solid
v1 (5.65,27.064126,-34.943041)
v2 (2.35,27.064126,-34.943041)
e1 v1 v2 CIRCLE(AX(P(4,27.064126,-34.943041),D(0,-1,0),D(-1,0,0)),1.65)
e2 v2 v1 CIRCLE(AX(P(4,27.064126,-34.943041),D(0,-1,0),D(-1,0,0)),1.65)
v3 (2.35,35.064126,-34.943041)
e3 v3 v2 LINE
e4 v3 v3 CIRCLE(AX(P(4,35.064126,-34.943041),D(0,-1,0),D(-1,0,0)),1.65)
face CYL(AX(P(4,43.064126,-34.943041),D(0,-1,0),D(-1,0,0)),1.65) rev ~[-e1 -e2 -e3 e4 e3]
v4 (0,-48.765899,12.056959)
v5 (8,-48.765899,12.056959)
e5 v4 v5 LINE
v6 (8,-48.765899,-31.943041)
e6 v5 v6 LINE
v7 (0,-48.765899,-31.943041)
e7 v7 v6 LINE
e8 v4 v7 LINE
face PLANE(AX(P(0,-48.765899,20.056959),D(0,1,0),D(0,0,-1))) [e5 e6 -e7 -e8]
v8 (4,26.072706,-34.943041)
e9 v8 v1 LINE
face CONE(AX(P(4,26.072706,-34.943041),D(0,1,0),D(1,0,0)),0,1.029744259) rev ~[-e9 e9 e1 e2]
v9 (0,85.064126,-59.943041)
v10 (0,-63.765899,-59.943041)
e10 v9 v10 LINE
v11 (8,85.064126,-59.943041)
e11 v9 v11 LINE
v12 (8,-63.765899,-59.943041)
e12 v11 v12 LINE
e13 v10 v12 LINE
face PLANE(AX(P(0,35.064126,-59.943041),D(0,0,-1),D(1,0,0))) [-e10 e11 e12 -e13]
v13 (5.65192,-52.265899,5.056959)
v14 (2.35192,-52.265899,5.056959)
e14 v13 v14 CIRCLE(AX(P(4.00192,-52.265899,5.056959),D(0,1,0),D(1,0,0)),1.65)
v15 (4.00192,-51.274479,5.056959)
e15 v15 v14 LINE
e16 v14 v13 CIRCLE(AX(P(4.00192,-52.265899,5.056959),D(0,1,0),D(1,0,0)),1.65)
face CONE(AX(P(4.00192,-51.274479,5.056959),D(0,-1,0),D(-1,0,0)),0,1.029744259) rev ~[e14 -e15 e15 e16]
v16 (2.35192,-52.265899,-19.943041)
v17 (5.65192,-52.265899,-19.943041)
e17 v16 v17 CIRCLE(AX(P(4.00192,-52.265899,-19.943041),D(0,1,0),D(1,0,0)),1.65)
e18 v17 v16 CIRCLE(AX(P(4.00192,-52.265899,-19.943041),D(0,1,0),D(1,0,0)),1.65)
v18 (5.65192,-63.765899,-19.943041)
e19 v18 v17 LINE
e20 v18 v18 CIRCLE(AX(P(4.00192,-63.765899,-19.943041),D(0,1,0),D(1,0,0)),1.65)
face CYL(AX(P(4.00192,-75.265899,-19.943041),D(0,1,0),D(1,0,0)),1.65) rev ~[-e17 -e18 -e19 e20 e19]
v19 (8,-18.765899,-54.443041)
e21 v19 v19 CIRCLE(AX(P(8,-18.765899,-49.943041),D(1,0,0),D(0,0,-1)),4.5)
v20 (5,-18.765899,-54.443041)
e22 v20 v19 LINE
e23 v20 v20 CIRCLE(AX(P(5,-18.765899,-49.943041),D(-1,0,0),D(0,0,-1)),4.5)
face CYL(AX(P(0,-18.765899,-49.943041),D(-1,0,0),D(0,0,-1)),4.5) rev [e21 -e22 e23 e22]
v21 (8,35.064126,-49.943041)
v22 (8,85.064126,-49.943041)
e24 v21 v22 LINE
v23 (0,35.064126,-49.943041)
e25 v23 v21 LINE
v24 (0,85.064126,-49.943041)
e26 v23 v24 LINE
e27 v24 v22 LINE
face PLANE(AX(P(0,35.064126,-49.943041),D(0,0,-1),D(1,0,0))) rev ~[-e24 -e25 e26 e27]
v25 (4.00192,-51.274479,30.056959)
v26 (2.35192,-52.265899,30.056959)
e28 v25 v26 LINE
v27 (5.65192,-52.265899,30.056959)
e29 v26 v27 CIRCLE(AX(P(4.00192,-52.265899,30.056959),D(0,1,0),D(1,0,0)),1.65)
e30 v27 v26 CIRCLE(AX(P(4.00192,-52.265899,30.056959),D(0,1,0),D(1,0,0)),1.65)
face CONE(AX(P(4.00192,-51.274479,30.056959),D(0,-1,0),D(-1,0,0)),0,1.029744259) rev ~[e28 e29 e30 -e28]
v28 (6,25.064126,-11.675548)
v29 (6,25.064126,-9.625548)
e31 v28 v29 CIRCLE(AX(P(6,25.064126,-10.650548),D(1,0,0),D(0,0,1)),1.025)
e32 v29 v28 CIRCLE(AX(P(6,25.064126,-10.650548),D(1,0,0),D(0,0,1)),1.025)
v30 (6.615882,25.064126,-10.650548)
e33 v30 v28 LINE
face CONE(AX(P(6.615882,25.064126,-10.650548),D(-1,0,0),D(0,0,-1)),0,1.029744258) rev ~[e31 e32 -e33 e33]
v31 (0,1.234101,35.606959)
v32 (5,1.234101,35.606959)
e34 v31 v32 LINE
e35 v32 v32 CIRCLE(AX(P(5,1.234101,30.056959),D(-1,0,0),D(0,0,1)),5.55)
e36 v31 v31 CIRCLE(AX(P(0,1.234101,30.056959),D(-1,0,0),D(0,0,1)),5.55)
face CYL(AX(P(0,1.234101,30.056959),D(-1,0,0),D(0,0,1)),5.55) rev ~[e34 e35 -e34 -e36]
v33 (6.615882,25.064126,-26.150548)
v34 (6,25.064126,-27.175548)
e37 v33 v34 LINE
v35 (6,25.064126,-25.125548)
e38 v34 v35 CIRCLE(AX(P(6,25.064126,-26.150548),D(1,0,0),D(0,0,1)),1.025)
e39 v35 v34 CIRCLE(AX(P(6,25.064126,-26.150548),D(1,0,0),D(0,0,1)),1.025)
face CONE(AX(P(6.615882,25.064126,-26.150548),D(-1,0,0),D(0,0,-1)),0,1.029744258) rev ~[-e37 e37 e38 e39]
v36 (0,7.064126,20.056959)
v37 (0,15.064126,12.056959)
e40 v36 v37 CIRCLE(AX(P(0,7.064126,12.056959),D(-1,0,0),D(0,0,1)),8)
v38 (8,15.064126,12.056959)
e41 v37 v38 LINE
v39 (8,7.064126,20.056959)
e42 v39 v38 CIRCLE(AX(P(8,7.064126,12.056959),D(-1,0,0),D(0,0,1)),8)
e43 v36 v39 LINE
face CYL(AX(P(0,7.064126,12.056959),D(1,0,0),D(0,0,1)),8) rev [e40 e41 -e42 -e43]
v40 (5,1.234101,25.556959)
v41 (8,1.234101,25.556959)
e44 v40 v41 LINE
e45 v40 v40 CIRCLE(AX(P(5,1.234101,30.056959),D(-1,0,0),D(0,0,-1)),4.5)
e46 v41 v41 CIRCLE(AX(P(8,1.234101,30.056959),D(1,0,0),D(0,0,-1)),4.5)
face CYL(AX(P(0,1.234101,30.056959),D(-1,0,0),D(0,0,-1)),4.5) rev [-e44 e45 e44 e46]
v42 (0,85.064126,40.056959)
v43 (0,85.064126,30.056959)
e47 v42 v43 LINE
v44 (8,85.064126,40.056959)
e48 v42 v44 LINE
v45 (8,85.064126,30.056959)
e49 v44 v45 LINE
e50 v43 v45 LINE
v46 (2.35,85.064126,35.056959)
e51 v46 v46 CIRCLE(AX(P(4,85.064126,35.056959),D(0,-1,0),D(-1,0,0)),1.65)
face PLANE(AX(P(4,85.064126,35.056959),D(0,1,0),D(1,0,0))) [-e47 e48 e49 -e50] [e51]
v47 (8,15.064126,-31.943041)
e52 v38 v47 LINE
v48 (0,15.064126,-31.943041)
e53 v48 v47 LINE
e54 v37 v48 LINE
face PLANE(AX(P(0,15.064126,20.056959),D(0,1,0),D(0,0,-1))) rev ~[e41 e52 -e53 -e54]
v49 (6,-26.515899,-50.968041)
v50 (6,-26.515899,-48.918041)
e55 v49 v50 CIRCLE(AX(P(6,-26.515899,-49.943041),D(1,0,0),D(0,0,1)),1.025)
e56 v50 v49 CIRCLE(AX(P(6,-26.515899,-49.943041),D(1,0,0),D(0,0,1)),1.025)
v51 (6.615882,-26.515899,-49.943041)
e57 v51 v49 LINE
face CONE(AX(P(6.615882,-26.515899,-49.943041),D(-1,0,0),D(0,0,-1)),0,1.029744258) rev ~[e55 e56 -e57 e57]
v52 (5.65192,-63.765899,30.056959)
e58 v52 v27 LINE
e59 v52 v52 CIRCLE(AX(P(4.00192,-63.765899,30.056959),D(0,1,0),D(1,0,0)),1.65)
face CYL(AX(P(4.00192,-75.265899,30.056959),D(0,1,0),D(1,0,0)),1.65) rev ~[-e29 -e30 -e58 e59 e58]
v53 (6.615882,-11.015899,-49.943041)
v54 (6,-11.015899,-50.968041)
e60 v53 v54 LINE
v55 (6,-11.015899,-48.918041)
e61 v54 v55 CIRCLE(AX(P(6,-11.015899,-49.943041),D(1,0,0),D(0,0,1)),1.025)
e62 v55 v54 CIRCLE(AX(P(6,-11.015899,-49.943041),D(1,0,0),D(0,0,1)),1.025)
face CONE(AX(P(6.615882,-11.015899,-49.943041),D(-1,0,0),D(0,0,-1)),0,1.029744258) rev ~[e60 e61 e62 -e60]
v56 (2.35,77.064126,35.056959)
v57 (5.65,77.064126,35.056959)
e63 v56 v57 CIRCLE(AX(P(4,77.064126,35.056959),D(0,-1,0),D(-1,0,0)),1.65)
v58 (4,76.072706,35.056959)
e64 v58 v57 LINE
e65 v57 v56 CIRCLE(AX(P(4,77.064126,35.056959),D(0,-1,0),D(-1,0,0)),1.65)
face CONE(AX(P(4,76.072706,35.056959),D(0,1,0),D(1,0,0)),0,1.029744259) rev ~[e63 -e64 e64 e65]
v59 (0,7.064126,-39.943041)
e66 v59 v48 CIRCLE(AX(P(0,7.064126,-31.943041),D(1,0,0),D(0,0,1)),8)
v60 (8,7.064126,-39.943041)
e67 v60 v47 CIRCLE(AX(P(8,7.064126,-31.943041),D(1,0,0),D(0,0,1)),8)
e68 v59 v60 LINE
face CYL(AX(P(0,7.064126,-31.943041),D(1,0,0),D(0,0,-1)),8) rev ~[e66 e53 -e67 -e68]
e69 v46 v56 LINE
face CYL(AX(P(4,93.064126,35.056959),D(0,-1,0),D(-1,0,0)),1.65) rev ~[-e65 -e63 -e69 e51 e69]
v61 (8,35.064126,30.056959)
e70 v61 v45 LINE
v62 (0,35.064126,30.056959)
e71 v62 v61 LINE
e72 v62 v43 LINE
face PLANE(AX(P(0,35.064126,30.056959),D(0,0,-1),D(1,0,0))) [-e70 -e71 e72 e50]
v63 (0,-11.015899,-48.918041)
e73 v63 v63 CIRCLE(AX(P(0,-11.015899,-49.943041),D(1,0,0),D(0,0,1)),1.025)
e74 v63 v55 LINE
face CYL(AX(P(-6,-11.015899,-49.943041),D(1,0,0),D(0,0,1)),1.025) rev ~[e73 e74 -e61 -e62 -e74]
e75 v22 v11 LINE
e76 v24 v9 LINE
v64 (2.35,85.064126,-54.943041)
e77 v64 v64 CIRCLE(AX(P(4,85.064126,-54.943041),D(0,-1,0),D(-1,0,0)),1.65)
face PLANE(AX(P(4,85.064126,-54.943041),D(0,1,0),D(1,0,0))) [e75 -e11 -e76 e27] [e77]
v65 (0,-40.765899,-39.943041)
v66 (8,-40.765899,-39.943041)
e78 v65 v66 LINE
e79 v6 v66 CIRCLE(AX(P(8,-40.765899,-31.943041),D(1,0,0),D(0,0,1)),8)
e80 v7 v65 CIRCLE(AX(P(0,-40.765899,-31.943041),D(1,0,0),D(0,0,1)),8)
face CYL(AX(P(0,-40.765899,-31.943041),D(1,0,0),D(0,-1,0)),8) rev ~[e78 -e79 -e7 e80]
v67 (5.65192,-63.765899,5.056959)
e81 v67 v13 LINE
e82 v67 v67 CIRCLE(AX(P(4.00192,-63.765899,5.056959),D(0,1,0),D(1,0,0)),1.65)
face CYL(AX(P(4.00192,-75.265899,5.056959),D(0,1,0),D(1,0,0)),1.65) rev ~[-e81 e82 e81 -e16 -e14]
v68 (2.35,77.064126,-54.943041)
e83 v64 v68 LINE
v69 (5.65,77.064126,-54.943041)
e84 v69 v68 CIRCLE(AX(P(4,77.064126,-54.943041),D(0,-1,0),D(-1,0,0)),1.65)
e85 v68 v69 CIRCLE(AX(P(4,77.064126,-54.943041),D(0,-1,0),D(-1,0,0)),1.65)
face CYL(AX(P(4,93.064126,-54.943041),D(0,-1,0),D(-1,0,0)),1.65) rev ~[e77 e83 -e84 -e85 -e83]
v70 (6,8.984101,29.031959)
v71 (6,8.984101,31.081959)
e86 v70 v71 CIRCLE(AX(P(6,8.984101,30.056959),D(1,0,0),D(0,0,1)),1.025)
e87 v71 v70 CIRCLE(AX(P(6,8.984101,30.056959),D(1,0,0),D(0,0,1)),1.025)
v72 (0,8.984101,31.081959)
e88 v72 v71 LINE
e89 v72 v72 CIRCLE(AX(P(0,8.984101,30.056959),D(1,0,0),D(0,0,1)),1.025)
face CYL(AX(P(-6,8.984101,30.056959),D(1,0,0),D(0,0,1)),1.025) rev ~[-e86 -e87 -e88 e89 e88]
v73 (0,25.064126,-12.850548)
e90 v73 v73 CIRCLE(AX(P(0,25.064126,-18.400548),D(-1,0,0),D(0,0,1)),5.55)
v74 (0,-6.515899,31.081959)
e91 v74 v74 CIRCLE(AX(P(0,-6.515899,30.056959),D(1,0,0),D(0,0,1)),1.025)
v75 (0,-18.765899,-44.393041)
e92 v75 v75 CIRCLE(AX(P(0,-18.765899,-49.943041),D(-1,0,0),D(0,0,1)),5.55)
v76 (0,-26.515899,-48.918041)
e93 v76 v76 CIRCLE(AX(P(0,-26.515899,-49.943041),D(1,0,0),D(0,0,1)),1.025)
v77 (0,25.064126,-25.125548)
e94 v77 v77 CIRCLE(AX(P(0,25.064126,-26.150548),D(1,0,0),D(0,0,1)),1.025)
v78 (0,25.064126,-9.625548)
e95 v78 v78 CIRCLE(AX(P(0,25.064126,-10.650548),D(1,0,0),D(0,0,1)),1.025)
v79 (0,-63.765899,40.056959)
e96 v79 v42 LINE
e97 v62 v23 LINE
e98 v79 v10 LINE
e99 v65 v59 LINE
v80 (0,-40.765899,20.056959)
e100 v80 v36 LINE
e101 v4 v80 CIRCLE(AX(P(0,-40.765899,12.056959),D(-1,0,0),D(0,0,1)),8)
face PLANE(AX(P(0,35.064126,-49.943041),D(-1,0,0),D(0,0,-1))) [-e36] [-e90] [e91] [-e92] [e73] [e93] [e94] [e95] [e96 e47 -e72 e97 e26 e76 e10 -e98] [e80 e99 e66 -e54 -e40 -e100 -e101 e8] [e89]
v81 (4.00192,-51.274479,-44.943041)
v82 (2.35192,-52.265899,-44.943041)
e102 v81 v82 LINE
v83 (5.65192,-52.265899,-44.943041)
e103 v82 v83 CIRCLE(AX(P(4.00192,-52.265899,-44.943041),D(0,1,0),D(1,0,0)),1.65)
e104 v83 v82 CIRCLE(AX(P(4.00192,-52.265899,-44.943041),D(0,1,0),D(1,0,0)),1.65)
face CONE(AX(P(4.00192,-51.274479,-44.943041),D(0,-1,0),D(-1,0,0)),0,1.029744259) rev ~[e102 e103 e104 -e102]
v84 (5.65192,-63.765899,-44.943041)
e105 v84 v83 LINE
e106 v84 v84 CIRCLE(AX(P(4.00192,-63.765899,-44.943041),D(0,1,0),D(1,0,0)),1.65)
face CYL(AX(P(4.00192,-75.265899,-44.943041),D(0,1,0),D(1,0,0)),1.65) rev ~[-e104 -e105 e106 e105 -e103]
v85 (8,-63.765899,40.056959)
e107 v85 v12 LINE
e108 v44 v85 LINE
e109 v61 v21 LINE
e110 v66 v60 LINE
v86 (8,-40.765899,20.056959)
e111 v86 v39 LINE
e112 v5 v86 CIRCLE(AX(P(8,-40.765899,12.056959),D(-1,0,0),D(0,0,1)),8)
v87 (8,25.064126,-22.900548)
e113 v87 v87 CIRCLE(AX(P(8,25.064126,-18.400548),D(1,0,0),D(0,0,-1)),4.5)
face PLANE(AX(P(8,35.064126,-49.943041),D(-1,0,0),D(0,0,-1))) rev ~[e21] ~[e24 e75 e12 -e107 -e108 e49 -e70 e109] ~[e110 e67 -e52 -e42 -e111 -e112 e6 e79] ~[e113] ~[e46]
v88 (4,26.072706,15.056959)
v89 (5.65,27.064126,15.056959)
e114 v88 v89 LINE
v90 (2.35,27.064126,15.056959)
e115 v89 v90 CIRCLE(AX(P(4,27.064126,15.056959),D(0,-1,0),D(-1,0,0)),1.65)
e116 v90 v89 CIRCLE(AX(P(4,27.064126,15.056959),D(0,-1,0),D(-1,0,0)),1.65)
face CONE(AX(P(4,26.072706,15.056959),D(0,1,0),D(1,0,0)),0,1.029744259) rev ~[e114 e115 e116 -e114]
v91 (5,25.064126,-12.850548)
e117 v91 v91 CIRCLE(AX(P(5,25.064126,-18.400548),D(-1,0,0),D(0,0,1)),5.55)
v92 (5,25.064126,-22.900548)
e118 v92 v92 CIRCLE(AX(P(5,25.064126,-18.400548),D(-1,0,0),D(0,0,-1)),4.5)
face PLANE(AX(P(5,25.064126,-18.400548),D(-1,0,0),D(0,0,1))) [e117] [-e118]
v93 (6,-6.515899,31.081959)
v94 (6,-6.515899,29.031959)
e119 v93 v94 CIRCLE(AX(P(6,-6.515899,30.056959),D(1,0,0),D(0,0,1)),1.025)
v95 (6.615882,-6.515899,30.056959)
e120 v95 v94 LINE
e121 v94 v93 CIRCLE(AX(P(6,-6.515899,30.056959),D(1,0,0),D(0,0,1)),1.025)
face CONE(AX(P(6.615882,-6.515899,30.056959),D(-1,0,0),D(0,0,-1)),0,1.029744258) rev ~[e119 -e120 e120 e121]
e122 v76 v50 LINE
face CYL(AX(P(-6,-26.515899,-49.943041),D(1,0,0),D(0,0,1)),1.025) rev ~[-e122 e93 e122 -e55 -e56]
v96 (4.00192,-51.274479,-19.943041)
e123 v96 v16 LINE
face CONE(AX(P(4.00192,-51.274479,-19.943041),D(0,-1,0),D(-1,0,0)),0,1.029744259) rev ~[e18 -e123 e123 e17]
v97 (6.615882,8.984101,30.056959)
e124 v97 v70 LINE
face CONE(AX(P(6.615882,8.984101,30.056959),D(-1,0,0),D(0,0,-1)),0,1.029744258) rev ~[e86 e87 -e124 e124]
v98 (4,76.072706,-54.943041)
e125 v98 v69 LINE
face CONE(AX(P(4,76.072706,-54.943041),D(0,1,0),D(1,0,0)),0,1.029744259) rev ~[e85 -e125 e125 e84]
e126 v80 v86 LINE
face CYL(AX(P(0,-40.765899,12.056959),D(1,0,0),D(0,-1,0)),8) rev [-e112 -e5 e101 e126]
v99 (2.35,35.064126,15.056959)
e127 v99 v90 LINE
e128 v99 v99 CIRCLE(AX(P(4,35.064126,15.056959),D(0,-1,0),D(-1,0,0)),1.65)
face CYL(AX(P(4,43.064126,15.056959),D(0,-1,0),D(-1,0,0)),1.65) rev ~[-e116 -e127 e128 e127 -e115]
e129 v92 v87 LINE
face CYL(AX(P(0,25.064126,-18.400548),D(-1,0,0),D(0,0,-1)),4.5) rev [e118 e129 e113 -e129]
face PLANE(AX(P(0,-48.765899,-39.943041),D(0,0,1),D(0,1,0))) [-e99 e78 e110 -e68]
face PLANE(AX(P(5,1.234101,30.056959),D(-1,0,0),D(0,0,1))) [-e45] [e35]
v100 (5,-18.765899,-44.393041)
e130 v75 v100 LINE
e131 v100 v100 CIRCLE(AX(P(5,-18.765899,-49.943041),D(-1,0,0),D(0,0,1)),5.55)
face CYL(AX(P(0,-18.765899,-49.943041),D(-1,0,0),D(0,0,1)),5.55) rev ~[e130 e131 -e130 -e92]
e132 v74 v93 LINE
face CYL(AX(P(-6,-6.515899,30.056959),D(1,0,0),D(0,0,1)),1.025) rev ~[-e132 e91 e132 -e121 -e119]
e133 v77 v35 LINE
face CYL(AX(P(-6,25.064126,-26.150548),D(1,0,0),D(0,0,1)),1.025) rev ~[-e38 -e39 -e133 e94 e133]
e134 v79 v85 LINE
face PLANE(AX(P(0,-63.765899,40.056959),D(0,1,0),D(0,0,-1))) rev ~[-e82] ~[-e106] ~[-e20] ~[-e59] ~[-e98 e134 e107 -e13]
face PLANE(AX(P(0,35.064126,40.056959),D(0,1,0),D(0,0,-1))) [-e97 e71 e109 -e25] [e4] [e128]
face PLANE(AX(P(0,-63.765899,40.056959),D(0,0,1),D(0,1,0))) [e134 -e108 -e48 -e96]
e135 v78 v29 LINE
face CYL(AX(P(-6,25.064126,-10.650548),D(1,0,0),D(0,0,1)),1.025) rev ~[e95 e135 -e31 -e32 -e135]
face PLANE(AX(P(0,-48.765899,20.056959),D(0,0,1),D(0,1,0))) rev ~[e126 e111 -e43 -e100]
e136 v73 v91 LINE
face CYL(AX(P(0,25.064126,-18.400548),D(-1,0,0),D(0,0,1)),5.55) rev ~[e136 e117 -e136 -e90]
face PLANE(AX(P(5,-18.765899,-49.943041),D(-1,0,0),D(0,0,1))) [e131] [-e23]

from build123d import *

# Parameters (mm, degrees)
SKETCH1_W               = 100
SKETCH1_H               = 98.830024952
SKETCH1_R               = 4.5
SKETCH1_W_2             = 60
SKETCH1_H_2             = 63.830024952
BOSS_EXTRUDE1_DEPTH     = 8
SKETCH4_R               = 5.55
CUT_EXTRUDE2_DEPTH      = 5
FILLET2_R               = 8
M2_5_TAPPED_HOLE1_D     = 2.05
M2_5_TAPPED_HOLE1_DEPTH = 6
M2_5_TAPPED_HOLE1_TIP   = 0.615882135
SKETCH11_R              = 1
CUT_EXTRUDE3_DEPTH      = 10
M4_TAPPED_HOLE1_D       = 3.3
M4_TAPPED_HOLE1_DEPTH   = 11.5
M4_TAPPED_HOLE1_TIP     = 0.991420021
SKETCH21_W              = 8
SKETCH21_H              = 10
BOSS_EXTRUDE2_DEPTH     = 50
M4_TAPPED_HOLE5_D       = 3.3
M4_TAPPED_HOLE5_DEPTH   = 8
M4_TAPPED_HOLE5_TIP     = 0.991420021
M4_TAPPED_HOLE6_D       = 3.3
M4_TAPPED_HOLE6_DEPTH   = 8
M4_TAPPED_HOLE6_TIP     = 0.991420021


with BuildPart() as part:
    # Sketch1 → Boss-Extrude1 (new body)
    with BuildSketch(Plane(origin=(0, 0, 0), x_dir=(0, 0, -1), z_dir=(1, 0, 0))):
        with Locations((9.943041263, -14.350886945)):
            Rectangle(SKETCH1_W, SKETCH1_H)
        with Locations((-30.056958737, 1.234100579)):
            Circle(SKETCH1_R, mode=Mode.SUBTRACT)
        with Locations((18.400547501, 25.064125531)):
            Circle(SKETCH1_R, mode=Mode.SUBTRACT)
        with Locations((49.943041263, -18.765899421)):
            Circle(SKETCH1_R, mode=Mode.SUBTRACT)
        with Locations((9.943041263, -16.850886945)):
            Rectangle(SKETCH1_W_2, SKETCH1_H_2, mode=Mode.SUBTRACT)
    extrude(amount=BOSS_EXTRUDE1_DEPTH)

    # Sketch4 → Cut-Extrude2 (cut)
    with BuildSketch(Plane.ZY):
        with Locations((-18.400547501, 25.064125531)):
            Circle(SKETCH4_R)
        with Locations((30.056958737, 1.234100579)):
            Circle(SKETCH4_R)
        with Locations((-49.943041263, -18.765899421)):
            Circle(SKETCH4_R)
    extrude(amount=-CUT_EXTRUDE2_DEPTH, mode=Mode.SUBTRACT)

    # Fillet2
    fillet2_edges = [part.edges().sort_by_distance(p)[0] for p in [
        (4, 15.064125531, 20.056958737),
        (4, -48.765899421, 20.056958737),
        (4, -48.765899421, -39.943041263),
        (4, 15.064125531, -39.943041263),
    ]]
    fillet(fillet2_edges, radius=FILLET2_R)

    # M2.5 Tapped Hole1
    with Locations(Plane(origin=(0, 25.064125531, -26.150547501), x_dir=(0, 0, -1), z_dir=(-1, 0, 0))):
        with Locations((0, 0), (-15.5, 0), (23.792493762, 36.080024952), (23.792493762, 51.580024952), (-56.207506238, 16.080024952), (-56.207506238, 31.580024952)):
            Hole(M2_5_TAPPED_HOLE1_D / 2, depth=M2_5_TAPPED_HOLE1_DEPTH)
            with Locations((0, 0, -(M2_5_TAPPED_HOLE1_DEPTH + M2_5_TAPPED_HOLE1_TIP / 2))):  # 118° drill point
                Cone(0, M2_5_TAPPED_HOLE1_D / 2, M2_5_TAPPED_HOLE1_TIP, mode=Mode.SUBTRACT)

    # Sketch11 → Cut-Extrude3 (cut)
    with BuildSketch(Plane.XZ.offset(63.765899421)):
        with Locations(Location((4.001919783, -44.943041263, 0), (0, 0, 270))):
            Circle(SKETCH11_R)
        with Locations(Location((4.001919783, 30.056958737, 0), (0, 0, 270))):
            Circle(SKETCH11_R)
        with Locations(Location((4.001919783, -19.943041263, 0), (0, 0, 270))):
            Circle(SKETCH11_R)
        with Locations(Location((4.001919783, 5.056958737, 0), (0, 0, 270))):
            Circle(SKETCH11_R)
    extrude(amount=-CUT_EXTRUDE3_DEPTH, mode=Mode.SUBTRACT)

    # M4 Tapped Hole1
    with Locations(Plane(origin=(0, -63.765899421, 0), x_dir=(-1, 0, 0), z_dir=(0, -1, 0))):
        with Locations((-4.001919783, 44.943041263), (-4.001919783, 19.943041263), (-4.001919783, -5.056958737), (-4.001919783, -30.056958737)):
            Hole(M4_TAPPED_HOLE1_D / 2, depth=M4_TAPPED_HOLE1_DEPTH)
            with Locations((0, 0, -(M4_TAPPED_HOLE1_DEPTH + M4_TAPPED_HOLE1_TIP / 2))):  # 118° drill point
                Cone(0, M4_TAPPED_HOLE1_D / 2, M4_TAPPED_HOLE1_TIP, mode=Mode.SUBTRACT)

    # Sketch21 → Boss-Extrude2 (add)
    with BuildSketch(Plane(origin=(0, 35.064125531, 0), x_dir=(1, 0, 0), z_dir=(0, 1, 0))):
        with Locations((4, 54.943041263)):
            Rectangle(SKETCH21_W, SKETCH21_H)
        with Locations((4, -35.056958737)):
            Rectangle(SKETCH21_W, SKETCH21_H)
    extrude(amount=BOSS_EXTRUDE2_DEPTH)

    # M4 Tapped Hole5
    with Locations(Plane(origin=(0, 85.064125531, 0), x_dir=(1, 0, 0), z_dir=(0, 1, 0))):
        with Locations((4, 54.943041263), (4, -35.056958737)):
            Hole(M4_TAPPED_HOLE5_D / 2, depth=M4_TAPPED_HOLE5_DEPTH)
            with Locations((0, 0, -(M4_TAPPED_HOLE5_DEPTH + M4_TAPPED_HOLE5_TIP / 2))):  # 118° drill point
                Cone(0, M4_TAPPED_HOLE5_D / 2, M4_TAPPED_HOLE5_TIP, mode=Mode.SUBTRACT)

    # M4 Tapped Hole6
    with Locations(Plane(origin=(0, 35.064125531, 0), x_dir=(1, 0, 0), z_dir=(0, 1, 0))):
        with Locations((4, 34.943041263), (4, -15.056958737)):
            Hole(M4_TAPPED_HOLE6_D / 2, depth=M4_TAPPED_HOLE6_DEPTH)
            with Locations((0, 0, -(M4_TAPPED_HOLE6_DEPTH + M4_TAPPED_HOLE6_TIP / 2))):  # 118° drill point
                Cone(0, M4_TAPPED_HOLE6_D / 2, M4_TAPPED_HOLE6_TIP, mode=Mode.SUBTRACT)


solid = part.part
